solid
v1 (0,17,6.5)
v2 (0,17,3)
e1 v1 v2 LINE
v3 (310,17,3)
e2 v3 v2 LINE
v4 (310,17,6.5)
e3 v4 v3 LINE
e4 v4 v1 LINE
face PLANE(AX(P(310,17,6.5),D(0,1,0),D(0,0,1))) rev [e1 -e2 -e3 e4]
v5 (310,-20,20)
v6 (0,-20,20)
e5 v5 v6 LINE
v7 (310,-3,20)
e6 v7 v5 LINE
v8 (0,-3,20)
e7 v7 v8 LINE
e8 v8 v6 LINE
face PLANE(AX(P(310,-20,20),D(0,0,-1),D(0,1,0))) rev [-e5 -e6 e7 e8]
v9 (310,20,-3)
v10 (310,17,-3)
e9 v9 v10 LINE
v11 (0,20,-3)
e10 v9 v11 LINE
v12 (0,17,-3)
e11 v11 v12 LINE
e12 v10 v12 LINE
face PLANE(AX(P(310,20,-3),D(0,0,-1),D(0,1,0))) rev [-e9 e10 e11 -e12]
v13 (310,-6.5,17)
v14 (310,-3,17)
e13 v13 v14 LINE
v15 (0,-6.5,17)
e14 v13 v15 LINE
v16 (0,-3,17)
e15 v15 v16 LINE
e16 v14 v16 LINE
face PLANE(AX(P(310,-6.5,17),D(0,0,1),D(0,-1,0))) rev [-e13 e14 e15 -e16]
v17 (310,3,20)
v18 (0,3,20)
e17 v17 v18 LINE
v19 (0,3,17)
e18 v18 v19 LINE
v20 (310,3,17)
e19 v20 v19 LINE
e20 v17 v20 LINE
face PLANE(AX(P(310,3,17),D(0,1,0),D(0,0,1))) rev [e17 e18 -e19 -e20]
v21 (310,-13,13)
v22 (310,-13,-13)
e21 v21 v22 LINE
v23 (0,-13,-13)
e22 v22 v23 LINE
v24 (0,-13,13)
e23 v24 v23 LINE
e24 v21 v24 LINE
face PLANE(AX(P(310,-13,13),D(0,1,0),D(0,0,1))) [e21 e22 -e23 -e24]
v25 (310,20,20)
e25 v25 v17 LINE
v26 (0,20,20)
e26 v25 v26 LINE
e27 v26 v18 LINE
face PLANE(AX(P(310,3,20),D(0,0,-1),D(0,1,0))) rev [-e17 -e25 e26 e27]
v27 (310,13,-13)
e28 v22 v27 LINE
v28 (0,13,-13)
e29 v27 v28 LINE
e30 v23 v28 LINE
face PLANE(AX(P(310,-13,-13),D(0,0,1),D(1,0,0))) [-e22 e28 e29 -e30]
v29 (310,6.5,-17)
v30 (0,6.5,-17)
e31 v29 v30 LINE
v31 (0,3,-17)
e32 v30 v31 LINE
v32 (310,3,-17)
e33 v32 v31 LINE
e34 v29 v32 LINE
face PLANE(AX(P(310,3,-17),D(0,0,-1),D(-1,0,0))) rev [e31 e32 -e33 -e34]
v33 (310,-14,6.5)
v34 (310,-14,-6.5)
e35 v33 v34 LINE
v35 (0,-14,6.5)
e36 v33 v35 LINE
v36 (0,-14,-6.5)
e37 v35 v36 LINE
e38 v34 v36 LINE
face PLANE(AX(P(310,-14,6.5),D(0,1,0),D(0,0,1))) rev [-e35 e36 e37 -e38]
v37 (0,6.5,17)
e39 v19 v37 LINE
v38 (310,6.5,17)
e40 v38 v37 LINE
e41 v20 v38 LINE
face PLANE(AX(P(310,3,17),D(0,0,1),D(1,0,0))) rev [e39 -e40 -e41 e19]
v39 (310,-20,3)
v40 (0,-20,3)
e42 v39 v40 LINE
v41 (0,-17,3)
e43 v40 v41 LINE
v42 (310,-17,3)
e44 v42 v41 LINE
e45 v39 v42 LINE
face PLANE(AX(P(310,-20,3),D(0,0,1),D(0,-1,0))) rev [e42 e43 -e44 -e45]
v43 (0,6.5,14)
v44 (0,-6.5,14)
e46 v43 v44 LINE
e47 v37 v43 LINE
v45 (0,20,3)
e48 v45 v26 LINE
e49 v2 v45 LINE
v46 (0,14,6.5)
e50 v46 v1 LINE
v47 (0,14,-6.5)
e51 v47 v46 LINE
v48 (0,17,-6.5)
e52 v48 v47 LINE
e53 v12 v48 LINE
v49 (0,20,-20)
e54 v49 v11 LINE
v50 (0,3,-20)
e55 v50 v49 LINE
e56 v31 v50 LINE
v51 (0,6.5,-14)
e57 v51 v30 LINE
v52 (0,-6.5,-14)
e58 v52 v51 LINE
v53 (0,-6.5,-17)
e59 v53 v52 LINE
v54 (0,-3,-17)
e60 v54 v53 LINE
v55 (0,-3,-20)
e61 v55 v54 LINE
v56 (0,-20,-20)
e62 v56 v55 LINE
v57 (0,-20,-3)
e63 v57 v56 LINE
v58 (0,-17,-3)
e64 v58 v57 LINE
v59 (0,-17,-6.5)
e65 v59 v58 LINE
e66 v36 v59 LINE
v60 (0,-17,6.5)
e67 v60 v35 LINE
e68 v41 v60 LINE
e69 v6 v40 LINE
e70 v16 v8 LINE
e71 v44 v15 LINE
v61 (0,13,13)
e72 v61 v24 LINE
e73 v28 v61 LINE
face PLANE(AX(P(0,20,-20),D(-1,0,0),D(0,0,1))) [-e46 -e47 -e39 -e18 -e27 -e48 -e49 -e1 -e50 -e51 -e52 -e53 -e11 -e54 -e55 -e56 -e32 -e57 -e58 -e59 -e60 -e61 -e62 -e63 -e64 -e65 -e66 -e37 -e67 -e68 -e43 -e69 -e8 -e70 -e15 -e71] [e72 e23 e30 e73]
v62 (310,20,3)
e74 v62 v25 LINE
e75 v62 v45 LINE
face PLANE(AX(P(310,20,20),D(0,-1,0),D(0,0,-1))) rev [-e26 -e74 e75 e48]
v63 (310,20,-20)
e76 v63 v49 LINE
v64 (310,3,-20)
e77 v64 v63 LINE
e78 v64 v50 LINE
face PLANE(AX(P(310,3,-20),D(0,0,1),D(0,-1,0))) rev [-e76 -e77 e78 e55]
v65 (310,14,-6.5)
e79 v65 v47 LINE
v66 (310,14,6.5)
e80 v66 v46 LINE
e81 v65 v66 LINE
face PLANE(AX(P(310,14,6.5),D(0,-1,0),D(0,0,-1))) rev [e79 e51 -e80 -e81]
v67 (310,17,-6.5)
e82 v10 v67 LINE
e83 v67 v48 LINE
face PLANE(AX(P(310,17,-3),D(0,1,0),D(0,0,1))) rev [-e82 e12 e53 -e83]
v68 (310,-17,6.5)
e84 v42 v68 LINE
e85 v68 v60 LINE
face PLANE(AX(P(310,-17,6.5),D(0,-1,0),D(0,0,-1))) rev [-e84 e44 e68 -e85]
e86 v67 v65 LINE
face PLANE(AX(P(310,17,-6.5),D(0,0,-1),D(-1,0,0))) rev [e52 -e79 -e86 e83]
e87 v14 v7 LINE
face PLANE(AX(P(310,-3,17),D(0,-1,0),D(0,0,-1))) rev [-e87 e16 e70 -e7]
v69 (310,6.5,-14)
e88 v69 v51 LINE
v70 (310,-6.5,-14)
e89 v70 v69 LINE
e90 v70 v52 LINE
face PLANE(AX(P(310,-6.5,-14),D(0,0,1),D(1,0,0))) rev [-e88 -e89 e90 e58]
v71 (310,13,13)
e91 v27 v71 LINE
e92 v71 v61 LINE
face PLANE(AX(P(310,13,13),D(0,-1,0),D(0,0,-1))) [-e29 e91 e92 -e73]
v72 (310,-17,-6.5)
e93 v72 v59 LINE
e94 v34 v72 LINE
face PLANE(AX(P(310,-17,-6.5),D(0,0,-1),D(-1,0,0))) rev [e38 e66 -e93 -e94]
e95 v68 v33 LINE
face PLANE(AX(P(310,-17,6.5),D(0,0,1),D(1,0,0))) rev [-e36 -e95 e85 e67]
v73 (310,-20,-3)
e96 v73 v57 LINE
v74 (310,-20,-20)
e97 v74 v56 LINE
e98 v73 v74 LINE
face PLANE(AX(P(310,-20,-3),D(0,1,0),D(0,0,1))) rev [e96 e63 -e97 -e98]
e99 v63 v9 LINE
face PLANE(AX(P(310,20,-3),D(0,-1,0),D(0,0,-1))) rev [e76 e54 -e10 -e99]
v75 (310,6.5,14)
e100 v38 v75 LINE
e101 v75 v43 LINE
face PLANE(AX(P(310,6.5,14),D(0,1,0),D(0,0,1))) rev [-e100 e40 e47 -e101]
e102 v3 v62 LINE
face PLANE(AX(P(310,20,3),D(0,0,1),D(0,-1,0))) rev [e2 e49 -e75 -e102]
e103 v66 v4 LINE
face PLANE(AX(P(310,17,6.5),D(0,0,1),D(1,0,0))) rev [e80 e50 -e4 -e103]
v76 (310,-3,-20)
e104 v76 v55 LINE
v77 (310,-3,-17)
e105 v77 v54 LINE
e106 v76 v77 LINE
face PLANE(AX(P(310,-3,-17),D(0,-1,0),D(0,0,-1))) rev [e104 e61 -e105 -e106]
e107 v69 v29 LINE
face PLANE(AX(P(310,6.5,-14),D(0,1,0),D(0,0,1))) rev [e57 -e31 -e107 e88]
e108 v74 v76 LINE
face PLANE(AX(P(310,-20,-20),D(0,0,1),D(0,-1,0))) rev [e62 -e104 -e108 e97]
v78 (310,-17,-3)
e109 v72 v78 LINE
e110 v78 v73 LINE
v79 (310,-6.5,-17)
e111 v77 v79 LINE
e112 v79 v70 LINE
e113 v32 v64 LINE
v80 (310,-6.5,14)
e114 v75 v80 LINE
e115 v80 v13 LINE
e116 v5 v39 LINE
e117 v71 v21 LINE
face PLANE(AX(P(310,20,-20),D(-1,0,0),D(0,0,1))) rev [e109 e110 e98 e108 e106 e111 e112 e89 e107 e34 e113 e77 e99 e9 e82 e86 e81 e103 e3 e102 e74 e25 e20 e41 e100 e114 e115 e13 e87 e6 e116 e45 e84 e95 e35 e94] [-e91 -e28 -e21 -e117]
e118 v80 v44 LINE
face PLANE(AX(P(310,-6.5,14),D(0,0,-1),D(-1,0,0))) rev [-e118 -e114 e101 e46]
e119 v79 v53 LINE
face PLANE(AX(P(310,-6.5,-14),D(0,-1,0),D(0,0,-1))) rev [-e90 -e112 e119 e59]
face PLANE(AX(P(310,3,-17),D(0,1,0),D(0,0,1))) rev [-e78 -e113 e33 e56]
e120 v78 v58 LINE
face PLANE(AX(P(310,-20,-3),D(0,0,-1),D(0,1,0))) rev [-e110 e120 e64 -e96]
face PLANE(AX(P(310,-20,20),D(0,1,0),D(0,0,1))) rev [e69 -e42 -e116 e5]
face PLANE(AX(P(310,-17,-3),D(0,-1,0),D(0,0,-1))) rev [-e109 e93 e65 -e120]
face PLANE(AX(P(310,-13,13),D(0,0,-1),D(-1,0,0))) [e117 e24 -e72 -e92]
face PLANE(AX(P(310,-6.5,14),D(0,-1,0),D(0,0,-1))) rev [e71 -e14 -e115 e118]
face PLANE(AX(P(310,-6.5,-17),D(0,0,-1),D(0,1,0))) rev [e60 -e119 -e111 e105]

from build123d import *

# Parameters (mm, degrees)
SKETCH1_W           = 26
SKETCH1_H           = 26
BOSS_EXTRUDE1_DEPTH = 310


with BuildPart() as part:
    # Sketch1 → Boss-Extrude1 (new body)
    with BuildSketch(Plane(origin=(0, 0, 0), x_dir=(0, 0, -1), z_dir=(1, 0, 0))):
        Polygon((-20, -20), (-3, -20), (-3, -17), (-6.5, -17), (-6.5, -14), (6.5, -14), (6.5, -17), (3, -17), (3, -20), (20, -20), (20, -3), (17, -3), (17, -6.5), (14, -6.5), (14, 6.5), (17, 6.5), (17, 3), (20, 3), (20, 20), (3, 20), (3, 17), (6.5, 17), (6.5, 14), (-6.5, 14), (-6.5, 17), (-3, 17), (-3, 20), (-20, 20), (-20, 3), (-17, 3), (-17, 6.5), (-14, 6.5), (-14, -6.5), (-17, -6.5), (-17, -3), (-20, -3), align=None)
        Rectangle(SKETCH1_W, SKETCH1_H, mode=Mode.SUBTRACT)
    extrude(amount=BOSS_EXTRUDE1_DEPTH)


solid = part.part
